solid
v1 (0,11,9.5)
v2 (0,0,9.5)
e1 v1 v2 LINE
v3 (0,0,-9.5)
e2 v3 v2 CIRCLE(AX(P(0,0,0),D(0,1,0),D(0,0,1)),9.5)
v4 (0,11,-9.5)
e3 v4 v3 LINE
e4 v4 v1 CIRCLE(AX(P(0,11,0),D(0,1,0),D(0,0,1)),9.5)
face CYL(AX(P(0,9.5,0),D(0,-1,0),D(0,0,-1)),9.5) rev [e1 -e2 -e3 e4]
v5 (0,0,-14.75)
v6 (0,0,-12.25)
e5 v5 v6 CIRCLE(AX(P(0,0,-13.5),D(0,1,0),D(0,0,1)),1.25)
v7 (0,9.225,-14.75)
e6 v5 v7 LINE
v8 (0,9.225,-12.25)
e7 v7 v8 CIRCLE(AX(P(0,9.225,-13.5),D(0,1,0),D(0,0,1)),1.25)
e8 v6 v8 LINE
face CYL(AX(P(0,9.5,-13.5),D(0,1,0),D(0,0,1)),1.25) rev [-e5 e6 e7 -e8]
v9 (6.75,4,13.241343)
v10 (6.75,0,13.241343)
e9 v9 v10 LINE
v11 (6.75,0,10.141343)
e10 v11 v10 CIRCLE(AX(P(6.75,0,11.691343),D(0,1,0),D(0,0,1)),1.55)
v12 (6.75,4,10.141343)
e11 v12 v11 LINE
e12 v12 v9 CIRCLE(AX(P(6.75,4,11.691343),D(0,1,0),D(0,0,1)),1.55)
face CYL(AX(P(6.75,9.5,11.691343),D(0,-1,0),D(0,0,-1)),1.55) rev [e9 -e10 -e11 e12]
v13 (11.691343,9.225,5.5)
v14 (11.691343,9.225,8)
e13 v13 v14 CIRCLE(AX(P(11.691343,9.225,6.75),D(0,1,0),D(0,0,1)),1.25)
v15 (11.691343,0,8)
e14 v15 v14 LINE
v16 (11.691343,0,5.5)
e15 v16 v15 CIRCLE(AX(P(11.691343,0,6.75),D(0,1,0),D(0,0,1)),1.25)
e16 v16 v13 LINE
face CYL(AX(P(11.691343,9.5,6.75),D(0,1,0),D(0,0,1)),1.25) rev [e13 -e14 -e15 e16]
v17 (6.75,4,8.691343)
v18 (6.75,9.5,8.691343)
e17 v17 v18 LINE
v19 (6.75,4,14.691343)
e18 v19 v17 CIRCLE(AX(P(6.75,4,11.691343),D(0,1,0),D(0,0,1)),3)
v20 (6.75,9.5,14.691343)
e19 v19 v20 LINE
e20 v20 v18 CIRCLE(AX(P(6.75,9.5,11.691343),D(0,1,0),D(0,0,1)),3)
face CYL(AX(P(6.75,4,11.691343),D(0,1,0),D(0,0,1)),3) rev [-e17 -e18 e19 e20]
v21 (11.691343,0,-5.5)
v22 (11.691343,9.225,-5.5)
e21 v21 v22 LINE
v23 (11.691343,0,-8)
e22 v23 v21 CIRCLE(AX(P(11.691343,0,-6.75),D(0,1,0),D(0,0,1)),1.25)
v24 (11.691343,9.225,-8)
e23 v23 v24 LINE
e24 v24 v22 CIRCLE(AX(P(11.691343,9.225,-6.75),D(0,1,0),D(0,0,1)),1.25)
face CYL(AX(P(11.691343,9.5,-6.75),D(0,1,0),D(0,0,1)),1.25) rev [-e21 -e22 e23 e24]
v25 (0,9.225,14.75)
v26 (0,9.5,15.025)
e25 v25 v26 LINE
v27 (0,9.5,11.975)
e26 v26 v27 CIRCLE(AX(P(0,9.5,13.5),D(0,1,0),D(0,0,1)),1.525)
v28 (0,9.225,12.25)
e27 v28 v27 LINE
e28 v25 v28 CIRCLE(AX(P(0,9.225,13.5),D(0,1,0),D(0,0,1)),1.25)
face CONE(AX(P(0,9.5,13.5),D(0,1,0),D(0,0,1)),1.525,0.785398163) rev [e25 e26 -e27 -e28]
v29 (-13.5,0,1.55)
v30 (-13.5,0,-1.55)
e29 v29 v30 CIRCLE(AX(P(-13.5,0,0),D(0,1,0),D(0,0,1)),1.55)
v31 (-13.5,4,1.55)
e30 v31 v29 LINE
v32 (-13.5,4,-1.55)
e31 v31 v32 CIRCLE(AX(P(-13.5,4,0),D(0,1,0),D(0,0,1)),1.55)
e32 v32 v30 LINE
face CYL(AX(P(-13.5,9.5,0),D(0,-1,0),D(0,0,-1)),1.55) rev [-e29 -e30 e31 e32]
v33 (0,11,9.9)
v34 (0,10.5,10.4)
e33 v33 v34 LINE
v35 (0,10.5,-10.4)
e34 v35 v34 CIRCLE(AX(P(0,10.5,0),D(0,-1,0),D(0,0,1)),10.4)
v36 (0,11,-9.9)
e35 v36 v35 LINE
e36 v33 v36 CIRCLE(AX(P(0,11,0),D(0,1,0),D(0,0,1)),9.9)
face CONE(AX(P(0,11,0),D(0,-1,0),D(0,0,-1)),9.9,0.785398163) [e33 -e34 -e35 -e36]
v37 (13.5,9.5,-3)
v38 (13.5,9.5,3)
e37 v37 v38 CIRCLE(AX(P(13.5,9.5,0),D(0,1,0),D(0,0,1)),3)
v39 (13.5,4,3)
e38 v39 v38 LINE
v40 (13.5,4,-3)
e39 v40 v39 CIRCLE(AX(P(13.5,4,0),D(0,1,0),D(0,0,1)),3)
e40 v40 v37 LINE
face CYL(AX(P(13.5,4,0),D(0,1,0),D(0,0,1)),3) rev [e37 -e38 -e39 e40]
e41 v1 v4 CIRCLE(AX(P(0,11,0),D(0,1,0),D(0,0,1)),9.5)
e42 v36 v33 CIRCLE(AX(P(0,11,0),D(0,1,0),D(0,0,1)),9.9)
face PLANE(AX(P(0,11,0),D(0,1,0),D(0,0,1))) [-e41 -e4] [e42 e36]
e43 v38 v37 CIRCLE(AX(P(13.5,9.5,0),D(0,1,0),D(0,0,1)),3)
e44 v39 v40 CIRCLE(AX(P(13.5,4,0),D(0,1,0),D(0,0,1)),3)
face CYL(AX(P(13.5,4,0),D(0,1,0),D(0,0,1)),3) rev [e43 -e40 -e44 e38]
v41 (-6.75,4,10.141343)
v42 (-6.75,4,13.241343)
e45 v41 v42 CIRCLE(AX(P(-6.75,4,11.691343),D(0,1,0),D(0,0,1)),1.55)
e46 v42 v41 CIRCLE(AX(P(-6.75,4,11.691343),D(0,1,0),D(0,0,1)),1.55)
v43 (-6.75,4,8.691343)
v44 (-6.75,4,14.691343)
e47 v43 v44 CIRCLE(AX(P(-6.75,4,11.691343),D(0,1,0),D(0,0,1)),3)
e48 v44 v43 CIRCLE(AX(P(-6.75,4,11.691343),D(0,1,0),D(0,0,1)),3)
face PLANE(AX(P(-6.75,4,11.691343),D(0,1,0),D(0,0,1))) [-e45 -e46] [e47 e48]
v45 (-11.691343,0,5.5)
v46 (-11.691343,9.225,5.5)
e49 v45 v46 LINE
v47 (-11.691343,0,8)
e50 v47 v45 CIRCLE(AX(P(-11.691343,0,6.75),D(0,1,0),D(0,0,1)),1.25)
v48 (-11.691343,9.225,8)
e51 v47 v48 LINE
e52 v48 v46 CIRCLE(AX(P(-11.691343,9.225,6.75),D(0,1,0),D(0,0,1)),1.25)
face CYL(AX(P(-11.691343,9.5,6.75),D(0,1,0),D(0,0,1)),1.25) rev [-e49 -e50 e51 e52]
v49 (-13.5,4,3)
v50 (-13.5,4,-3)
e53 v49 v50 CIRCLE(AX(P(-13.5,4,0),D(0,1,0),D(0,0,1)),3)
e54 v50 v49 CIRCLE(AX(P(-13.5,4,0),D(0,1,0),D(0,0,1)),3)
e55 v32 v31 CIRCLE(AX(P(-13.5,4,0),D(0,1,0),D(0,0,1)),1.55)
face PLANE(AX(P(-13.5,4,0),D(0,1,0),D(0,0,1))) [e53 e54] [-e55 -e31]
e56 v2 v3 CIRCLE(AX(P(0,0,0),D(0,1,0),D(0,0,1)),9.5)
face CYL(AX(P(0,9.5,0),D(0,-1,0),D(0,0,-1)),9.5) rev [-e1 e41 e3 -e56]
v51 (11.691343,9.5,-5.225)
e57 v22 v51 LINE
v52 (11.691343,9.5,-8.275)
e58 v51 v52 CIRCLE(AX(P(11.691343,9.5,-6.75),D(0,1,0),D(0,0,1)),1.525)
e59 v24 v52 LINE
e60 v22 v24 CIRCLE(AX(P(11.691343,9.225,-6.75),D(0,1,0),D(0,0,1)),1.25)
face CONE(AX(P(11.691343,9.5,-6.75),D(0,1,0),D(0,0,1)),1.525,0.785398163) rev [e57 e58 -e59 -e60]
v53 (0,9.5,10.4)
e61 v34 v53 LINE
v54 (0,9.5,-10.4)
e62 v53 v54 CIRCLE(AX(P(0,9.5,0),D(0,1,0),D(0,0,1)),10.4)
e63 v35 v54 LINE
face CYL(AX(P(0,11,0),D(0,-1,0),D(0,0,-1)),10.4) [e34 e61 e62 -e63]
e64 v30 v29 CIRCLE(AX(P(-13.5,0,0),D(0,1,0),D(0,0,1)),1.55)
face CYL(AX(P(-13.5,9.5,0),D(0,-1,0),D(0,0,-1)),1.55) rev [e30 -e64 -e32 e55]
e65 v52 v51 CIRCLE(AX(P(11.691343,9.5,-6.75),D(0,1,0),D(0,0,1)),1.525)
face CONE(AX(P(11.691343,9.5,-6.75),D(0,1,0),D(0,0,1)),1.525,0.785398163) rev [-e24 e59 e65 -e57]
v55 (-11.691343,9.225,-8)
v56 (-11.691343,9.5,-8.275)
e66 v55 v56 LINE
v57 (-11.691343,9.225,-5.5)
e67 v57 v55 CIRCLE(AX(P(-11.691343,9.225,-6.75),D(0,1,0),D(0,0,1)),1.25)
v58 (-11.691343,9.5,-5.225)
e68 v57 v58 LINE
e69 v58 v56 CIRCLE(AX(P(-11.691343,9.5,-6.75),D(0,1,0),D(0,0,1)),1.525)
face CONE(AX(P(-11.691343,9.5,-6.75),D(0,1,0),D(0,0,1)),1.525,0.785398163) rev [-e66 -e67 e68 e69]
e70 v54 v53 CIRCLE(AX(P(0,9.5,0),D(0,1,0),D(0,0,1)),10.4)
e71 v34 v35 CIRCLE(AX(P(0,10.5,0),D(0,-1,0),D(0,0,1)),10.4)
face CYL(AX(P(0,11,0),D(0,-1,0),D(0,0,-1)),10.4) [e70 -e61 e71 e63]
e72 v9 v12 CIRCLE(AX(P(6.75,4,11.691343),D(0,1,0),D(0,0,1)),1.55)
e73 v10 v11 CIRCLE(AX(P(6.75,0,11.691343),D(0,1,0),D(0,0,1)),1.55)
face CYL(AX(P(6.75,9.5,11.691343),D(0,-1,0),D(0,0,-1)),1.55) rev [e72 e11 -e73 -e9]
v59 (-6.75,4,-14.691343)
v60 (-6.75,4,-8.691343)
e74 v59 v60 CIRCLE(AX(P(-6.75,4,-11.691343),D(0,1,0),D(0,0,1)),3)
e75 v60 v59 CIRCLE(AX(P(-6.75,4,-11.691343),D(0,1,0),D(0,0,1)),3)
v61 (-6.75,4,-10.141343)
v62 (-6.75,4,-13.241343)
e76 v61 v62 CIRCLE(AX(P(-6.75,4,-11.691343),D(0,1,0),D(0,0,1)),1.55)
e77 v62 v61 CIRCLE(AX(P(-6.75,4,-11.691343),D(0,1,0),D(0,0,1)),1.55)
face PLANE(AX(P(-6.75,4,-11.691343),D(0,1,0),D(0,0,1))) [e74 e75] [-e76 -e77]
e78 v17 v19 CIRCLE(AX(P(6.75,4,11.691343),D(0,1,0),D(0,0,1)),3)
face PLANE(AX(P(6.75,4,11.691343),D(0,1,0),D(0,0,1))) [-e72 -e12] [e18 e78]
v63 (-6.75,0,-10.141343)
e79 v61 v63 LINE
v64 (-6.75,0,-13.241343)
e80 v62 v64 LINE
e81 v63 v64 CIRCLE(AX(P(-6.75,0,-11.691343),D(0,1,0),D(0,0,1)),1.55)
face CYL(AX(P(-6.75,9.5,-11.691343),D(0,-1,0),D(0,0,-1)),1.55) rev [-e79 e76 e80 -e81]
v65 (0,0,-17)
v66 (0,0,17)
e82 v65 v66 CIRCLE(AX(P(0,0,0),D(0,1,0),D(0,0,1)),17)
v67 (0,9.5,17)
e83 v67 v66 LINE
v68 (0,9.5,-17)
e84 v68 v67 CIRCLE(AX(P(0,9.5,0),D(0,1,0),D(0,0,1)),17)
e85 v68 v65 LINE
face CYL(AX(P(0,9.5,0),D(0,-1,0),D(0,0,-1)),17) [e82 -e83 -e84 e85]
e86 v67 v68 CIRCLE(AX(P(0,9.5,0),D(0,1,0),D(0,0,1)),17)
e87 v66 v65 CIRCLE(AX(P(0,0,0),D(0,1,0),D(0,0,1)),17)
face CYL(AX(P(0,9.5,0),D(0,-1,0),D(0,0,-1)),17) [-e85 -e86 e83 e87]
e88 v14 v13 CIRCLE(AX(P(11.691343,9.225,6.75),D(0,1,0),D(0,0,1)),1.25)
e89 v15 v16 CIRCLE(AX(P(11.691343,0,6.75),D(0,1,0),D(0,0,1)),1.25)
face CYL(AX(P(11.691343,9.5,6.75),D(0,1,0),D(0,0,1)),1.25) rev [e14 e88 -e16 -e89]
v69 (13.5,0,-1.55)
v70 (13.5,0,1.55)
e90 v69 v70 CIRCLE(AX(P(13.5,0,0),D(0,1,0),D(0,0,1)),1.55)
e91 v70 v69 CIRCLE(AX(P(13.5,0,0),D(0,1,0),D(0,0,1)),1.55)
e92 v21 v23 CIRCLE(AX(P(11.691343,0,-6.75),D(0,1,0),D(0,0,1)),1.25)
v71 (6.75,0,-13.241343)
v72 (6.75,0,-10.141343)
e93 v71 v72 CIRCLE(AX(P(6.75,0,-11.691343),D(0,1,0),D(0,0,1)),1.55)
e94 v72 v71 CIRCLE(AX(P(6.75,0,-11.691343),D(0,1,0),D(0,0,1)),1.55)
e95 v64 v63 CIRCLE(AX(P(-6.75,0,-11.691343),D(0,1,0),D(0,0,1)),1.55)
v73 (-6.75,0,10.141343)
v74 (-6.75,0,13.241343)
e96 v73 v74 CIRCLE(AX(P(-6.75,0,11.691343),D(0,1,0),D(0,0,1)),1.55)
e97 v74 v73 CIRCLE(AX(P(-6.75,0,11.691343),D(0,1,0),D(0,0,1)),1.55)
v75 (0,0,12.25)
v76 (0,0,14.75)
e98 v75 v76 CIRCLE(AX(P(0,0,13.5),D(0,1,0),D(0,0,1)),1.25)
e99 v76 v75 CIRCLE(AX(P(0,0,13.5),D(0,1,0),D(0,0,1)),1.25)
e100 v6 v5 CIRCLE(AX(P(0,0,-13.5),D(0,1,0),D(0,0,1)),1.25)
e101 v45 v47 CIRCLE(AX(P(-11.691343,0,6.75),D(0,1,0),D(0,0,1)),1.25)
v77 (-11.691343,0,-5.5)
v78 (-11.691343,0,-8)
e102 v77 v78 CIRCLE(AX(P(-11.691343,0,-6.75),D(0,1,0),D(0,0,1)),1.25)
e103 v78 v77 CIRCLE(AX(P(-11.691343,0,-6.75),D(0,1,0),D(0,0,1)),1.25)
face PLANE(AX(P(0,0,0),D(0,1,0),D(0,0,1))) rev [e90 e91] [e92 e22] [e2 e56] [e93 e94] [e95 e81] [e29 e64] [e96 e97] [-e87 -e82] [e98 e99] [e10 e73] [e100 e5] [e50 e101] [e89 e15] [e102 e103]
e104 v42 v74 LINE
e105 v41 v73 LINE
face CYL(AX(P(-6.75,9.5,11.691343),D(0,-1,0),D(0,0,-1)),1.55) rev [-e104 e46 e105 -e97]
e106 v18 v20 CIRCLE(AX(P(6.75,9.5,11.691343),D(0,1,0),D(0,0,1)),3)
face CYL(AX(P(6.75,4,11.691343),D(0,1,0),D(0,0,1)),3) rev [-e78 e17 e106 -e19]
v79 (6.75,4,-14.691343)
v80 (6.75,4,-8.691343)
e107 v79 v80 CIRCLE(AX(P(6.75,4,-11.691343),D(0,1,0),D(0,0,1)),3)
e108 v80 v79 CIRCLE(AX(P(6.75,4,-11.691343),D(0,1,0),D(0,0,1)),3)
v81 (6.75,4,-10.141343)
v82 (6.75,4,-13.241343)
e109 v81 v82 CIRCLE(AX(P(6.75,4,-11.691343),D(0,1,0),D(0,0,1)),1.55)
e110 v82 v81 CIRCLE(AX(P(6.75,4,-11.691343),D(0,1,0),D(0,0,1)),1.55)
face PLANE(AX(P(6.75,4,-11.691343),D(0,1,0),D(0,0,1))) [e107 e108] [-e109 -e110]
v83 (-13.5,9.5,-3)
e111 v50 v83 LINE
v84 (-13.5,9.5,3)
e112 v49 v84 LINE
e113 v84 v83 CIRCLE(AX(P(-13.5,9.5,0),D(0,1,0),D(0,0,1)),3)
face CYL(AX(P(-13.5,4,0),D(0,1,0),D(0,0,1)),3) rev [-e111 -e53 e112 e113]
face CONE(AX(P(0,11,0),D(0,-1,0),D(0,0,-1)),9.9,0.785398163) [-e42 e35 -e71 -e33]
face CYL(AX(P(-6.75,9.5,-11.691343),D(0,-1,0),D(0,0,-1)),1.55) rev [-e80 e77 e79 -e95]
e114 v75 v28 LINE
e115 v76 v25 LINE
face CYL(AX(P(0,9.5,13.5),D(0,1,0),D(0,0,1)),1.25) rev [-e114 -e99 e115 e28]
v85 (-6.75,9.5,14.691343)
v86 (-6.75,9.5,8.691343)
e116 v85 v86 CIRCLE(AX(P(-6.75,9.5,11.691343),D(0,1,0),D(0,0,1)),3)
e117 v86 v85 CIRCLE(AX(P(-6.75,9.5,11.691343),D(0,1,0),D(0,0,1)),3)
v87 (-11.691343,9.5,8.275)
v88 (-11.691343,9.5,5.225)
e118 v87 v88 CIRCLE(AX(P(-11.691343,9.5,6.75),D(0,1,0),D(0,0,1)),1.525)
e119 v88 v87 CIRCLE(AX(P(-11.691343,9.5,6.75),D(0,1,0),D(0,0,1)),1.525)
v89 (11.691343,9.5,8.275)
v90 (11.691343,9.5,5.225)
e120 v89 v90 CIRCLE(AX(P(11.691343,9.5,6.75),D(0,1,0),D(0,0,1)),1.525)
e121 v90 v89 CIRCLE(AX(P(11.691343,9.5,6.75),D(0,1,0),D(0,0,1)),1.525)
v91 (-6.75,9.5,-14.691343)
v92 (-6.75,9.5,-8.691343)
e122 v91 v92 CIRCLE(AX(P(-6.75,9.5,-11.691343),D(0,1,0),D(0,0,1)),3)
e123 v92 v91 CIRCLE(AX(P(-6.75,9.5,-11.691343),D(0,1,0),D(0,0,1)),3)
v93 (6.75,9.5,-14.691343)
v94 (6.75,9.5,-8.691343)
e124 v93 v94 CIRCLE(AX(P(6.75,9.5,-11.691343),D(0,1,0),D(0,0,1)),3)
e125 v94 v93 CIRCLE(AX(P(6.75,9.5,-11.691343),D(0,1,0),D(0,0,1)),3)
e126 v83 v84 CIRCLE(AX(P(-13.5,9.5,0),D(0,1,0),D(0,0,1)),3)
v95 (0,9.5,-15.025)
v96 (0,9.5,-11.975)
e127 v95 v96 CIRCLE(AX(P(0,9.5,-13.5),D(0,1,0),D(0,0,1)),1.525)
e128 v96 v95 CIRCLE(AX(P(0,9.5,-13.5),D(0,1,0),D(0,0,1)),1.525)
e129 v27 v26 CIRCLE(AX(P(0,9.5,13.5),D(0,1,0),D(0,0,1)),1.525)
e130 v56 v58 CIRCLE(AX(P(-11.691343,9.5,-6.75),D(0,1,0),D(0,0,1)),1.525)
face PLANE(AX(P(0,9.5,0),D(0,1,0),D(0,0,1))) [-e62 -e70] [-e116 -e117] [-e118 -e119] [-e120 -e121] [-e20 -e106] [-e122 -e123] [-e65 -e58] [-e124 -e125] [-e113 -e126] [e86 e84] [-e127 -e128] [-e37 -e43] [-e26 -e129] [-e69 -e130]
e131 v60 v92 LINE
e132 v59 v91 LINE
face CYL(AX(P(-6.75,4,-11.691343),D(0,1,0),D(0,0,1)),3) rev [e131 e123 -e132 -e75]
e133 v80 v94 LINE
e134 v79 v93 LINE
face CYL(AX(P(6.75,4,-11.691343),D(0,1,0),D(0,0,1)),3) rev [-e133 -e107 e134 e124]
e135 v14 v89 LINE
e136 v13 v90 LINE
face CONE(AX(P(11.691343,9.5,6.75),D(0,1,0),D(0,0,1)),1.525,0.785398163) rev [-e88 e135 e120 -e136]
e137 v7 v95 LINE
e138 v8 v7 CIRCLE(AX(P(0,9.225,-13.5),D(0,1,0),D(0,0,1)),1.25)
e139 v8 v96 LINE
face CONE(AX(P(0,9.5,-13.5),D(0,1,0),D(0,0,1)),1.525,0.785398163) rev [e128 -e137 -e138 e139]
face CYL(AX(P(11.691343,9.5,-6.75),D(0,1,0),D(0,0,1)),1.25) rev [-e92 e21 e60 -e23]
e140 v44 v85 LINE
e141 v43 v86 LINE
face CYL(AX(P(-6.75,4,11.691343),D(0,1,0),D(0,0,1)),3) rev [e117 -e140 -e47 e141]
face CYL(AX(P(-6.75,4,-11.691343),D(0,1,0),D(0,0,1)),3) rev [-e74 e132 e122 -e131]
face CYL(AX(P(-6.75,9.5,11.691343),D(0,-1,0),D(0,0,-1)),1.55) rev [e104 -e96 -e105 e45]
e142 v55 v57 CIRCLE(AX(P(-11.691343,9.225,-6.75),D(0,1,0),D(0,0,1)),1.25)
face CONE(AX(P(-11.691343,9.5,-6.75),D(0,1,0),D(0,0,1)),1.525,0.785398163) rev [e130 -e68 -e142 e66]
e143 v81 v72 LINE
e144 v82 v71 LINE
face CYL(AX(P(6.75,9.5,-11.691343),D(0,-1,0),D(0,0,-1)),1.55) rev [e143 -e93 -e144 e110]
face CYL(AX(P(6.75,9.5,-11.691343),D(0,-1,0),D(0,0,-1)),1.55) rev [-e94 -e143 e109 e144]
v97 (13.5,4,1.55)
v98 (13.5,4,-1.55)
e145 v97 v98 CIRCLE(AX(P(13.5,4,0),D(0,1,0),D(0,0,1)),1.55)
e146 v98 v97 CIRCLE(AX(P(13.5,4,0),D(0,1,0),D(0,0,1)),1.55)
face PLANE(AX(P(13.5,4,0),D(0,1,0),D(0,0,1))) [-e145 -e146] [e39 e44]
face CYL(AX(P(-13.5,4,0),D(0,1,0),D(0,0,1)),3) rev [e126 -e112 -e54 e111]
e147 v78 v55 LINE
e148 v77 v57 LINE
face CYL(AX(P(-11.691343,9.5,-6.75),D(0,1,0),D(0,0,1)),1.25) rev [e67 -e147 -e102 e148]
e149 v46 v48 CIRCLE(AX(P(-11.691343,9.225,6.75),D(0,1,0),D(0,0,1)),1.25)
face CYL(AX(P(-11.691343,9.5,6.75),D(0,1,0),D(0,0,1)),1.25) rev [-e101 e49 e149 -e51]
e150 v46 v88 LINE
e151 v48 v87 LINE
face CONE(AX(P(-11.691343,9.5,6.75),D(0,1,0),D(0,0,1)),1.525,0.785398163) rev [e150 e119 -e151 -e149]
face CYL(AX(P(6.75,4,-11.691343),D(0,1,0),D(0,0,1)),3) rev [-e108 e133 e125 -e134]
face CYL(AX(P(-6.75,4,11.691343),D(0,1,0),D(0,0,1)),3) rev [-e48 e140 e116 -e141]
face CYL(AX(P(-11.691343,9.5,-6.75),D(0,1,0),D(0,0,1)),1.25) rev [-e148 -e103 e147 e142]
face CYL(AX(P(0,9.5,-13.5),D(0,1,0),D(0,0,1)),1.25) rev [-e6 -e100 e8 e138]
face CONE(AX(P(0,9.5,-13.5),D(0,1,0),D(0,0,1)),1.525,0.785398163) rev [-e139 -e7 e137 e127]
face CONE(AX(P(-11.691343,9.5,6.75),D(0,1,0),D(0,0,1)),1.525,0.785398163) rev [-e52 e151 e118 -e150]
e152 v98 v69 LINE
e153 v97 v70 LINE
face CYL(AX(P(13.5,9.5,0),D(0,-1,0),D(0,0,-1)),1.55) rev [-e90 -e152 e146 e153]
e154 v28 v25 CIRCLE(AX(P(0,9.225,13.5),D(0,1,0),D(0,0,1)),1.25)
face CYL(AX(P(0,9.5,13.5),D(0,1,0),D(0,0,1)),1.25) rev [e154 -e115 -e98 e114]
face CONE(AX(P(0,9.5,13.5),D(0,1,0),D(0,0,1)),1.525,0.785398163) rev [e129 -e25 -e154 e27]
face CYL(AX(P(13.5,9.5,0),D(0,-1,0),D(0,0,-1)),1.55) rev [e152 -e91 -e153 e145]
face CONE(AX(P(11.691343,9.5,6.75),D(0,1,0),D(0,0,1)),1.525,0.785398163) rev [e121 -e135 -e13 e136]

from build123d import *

# Parameters (mm, degrees)
SKETCH_1_R                   = 17
SKETCH_1_R_2                 = 1.55
SKETCH_1_R_3                 = 9.5
EXTRUDE_1_DEPTH              = 9.5
HOLE_WIZARD_M3_1_D           = 2.5
HOLE_WIZARD_M3_1_CSINK_D     = 3.05
HOLE_WIZARD_M3_1_CSINK_ANGLE = 90
SKETCH_7_R                   = 10.4
SKETCH_7_R_2                 = 9.5
EXTRUDE_2_DEPTH              = 1.5
SKETCH_5_R                   = 3
CUT_EXTRUDE_1_DEPTH          = 5.5
CHAMFER_1_SIZE               = 0.5


with BuildPart() as part:
    # 草图1 → 凸台-拉伸1 (new body)
    with BuildSketch(Plane(origin=(0, 0, 0), x_dir=(1, 0, 0), z_dir=(0, 1, 0))):
        with Locations(Location((0, 0, 0), (0, 0, 270))):
            Circle(SKETCH_1_R)
        with Locations(Location((13.5, 0, 0), (0, 0, 270))):
            Circle(SKETCH_1_R_2, mode=Mode.SUBTRACT)
        with Locations(Location((6.75, -11.691342951, 0), (0, 0, 270))):
            Circle(SKETCH_1_R_2, mode=Mode.SUBTRACT)
        with Locations(Location((-6.75, -11.691342951, 0), (0, 0, 270))):
            Circle(SKETCH_1_R_2, mode=Mode.SUBTRACT)
        with Locations(Location((-13.5, 0, 0), (0, 0, 270))):
            Circle(SKETCH_1_R_2, mode=Mode.SUBTRACT)
        with Locations(Location((-6.75, 11.691342951, 0), (0, 0, 270))):
            Circle(SKETCH_1_R_2, mode=Mode.SUBTRACT)
        with Locations(Location((6.75, 11.691342951, 0), (0, 0, 270))):
            Circle(SKETCH_1_R_2, mode=Mode.SUBTRACT)
        with Locations(Location((0, 0, 0), (0, 0, 270))):
            Circle(SKETCH_1_R_3, mode=Mode.SUBTRACT)
    extrude(amount=EXTRUDE_1_DEPTH)

    # M3 螺纹孔1 (through all)
    with Locations(Plane(origin=(0, 9.5, 0), x_dir=(1, 0, 0), z_dir=(0, 1, 0))):
        with Locations((11.691342951, 6.75), (11.691342951, -6.75), (0, -13.5), (-11.691342951, -6.75), (-11.691342951, 6.75), (0, 13.5), (0, 0)):
            CounterSinkHole(HOLE_WIZARD_M3_1_D / 2, HOLE_WIZARD_M3_1_CSINK_D / 2, counter_sink_angle=HOLE_WIZARD_M3_1_CSINK_ANGLE)

    # 草图7 → 凸台-拉伸2 (add)
    with BuildSketch(Plane(origin=(0, 9.5, 0), x_dir=(1, 0, 0), z_dir=(0, 1, 0))):
        with Locations(Location((0, 0, 0), (0, 0, 270))):
            Circle(SKETCH_7_R)
        with Locations(Location((0, 0, 0), (0, 0, 270))):
            Circle(SKETCH_7_R_2, mode=Mode.SUBTRACT)
    extrude(amount=EXTRUDE_2_DEPTH)

    # 草图5 → 切除-拉伸1 (cut)
    with BuildSketch(Plane(origin=(0, 9.5, 0), x_dir=(1, 0, 0), z_dir=(0, 1, 0))):
        with Locations(Location((13.5, 0, 0), (0, 0, 270))):
            Circle(SKETCH_5_R)
        with Locations(Location((6.75, -11.691342951, 0), (0, 0, 270))):
            Circle(SKETCH_5_R)
        with Locations(Location((-6.75, -11.691342951, 0), (0, 0, 270))):
            Circle(SKETCH_5_R)
        with Locations(Location((-13.5, 0, 0), (0, 0, 270))):
            Circle(SKETCH_5_R)
        with Locations(Location((-6.75, 11.691342951, 0), (0, 0, 270))):
            Circle(SKETCH_5_R)
        with Locations(Location((6.75, 11.691342951, 0), (0, 0, 270))):
            Circle(SKETCH_5_R)
    extrude(amount=-CUT_EXTRUDE_1_DEPTH, mode=Mode.SUBTRACT)

    # 倒角1
    chamfer_1_edges = [part.edges().sort_by_distance(p)[0] for p in [
        (0, 11, -10.4),
    ]]
    chamfer(chamfer_1_edges, length=CHAMFER_1_SIZE)


solid = part.part
